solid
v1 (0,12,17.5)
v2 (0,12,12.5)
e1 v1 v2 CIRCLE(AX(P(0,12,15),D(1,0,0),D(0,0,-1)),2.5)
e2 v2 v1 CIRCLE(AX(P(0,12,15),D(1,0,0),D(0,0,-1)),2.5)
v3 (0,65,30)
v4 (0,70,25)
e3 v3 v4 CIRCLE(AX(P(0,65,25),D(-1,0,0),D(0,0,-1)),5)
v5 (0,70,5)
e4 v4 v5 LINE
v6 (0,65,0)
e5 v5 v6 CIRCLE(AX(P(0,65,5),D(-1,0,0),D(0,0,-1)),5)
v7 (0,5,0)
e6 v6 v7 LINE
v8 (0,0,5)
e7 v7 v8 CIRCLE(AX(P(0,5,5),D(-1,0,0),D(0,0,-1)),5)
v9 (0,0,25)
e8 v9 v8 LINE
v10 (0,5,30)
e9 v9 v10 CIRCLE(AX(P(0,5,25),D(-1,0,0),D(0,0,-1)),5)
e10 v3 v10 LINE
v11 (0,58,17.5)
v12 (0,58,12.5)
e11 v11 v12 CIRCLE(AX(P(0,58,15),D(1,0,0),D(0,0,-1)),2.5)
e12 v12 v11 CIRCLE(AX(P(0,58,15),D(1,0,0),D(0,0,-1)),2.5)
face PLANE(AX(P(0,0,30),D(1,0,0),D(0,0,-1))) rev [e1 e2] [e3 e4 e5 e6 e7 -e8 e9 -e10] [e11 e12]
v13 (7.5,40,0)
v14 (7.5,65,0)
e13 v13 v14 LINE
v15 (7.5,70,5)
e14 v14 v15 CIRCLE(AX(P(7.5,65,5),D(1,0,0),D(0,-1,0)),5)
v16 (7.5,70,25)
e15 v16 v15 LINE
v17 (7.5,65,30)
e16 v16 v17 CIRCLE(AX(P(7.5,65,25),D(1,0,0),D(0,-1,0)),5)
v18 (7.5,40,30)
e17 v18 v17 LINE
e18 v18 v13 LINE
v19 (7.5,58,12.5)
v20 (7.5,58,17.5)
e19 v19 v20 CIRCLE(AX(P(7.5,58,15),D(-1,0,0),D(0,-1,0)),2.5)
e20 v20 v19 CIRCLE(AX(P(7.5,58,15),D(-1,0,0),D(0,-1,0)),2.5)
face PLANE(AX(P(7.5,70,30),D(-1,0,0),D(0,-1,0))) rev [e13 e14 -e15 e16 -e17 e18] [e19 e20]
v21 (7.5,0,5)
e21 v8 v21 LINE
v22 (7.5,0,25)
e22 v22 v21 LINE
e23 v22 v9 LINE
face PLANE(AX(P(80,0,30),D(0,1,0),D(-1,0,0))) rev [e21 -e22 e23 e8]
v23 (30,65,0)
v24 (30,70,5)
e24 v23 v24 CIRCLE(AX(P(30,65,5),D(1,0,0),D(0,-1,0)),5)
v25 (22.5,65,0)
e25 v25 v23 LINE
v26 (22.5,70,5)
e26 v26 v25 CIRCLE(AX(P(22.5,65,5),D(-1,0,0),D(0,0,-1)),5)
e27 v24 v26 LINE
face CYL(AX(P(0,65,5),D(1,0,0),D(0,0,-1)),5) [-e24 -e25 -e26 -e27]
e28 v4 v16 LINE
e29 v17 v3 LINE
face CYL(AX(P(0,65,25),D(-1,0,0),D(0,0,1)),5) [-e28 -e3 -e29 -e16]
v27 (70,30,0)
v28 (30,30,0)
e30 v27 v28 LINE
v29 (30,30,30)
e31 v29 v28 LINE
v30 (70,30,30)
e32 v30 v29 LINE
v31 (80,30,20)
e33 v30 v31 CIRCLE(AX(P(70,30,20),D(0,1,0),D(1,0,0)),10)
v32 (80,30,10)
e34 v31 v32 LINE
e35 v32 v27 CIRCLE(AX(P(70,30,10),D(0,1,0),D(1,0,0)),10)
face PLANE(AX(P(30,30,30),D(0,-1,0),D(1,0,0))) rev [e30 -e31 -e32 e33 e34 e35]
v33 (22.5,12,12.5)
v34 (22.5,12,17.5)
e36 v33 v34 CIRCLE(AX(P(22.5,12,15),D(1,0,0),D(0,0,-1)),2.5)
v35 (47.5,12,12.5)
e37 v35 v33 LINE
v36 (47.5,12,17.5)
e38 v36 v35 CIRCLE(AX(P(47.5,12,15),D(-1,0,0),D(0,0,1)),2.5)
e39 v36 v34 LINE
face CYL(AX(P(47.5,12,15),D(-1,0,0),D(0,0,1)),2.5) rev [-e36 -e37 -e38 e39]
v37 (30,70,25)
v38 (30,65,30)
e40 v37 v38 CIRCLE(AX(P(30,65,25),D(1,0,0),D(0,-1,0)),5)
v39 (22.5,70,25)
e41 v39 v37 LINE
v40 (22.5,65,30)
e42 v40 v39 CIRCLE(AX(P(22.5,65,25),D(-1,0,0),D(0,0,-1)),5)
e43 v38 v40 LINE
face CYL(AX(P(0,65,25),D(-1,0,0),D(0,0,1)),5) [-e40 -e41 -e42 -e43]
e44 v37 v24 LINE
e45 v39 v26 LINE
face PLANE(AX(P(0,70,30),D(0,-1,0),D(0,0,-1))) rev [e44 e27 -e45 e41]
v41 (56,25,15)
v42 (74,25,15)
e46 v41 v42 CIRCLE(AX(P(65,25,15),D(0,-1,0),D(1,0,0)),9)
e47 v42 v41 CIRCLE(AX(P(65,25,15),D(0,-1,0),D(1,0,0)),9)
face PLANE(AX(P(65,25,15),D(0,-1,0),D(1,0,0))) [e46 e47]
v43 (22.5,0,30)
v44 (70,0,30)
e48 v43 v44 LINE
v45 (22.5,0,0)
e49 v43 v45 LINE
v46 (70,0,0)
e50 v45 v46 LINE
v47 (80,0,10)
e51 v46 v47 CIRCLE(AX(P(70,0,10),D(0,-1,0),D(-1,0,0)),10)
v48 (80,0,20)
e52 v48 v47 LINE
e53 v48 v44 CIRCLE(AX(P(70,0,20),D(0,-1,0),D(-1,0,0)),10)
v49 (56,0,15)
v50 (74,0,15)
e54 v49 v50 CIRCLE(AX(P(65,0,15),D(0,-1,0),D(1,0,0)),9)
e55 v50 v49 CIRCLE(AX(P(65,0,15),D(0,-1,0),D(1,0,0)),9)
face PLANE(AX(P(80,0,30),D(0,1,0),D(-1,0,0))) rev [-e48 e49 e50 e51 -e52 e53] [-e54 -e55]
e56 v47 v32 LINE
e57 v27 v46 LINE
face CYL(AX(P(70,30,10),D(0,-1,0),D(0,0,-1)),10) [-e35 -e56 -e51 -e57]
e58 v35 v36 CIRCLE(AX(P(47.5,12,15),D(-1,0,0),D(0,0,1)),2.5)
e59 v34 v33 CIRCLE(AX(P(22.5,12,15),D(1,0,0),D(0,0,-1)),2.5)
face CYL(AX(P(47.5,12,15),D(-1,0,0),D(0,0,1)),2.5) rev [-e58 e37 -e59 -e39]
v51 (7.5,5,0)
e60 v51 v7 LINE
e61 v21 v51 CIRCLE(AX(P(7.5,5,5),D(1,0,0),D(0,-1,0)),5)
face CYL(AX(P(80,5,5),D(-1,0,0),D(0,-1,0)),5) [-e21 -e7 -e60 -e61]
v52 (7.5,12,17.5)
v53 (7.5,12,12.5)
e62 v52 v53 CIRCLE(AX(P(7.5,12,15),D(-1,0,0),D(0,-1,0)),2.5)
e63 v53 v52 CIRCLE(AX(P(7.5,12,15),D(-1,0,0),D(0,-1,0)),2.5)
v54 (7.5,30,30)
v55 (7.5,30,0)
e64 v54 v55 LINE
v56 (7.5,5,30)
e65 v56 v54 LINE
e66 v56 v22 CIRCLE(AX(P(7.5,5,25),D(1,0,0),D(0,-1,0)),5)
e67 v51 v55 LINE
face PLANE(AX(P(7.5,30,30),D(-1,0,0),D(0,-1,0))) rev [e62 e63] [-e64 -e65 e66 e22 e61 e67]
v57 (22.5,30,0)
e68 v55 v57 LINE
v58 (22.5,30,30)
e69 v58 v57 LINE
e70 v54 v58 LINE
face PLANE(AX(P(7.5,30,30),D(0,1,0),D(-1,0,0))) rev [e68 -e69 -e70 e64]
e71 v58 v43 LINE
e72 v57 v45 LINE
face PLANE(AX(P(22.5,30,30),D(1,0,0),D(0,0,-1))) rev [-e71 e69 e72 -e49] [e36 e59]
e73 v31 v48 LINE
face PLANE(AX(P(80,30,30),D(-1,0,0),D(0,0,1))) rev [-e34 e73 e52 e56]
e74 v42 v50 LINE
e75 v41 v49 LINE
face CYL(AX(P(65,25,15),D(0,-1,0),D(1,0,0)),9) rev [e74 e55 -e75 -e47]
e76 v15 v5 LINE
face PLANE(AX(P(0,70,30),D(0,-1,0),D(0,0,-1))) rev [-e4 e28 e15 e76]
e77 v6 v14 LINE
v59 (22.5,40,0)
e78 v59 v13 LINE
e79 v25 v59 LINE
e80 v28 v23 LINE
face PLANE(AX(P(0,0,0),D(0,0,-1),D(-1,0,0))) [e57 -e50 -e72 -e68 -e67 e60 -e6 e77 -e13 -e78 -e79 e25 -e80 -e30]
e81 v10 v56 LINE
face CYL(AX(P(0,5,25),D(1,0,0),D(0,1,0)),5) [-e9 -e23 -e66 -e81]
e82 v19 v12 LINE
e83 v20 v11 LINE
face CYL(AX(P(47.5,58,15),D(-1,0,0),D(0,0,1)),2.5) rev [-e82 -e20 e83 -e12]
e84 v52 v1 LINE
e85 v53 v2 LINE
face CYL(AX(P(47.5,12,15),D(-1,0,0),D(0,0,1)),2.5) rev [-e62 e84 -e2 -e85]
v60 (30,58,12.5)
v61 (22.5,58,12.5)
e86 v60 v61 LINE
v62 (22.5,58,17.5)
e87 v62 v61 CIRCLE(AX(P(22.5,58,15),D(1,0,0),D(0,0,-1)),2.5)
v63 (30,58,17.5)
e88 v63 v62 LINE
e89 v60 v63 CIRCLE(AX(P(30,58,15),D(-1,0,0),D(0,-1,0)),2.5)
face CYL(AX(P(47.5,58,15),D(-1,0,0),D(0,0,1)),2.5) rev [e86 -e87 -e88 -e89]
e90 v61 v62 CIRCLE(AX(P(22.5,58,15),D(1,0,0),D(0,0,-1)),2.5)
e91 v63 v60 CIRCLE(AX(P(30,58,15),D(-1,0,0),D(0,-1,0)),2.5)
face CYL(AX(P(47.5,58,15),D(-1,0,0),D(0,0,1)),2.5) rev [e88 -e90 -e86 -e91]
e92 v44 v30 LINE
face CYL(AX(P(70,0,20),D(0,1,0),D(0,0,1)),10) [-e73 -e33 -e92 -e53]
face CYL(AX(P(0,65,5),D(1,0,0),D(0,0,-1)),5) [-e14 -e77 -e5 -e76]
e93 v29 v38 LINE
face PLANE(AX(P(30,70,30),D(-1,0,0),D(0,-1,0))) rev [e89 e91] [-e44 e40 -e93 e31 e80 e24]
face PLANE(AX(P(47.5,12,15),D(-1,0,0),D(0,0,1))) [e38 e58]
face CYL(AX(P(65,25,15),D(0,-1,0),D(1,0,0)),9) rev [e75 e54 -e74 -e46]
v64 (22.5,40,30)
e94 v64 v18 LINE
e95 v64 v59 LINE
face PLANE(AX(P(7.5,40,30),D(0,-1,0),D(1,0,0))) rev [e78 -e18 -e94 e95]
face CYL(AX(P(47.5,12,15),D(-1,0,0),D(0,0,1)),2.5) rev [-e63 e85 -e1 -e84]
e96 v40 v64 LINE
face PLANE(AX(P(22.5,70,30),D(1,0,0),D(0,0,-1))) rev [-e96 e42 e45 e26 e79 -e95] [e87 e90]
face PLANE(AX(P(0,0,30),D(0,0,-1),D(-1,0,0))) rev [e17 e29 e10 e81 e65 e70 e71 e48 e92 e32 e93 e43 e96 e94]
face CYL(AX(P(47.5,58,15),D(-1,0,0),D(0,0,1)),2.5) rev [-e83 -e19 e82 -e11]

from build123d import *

# Parameters (mm, degrees)
BOSS_EXTRUDE1_DEPTH = 30
SKETCH4_R           = 9
CUT_EXTRUDE2_DEPTH  = 25
SKETCH5_W           = 15
SKETCH5_H           = 30
CUT_EXTRUDE3_DEPTH  = 111.453610172
SKETCH6_R           = 2.5
CUT_EXTRUDE4_DEPTH  = 25
FILLET1_R           = 5
FILLET2_R           = 10


with BuildPart() as part:
    # Sketch1 → Boss-Extrude1 (new body)
    with BuildSketch(Plane.XY):
        Polygon((0, 0), (0, 70), (30, 70), (30, 30), (80, 30), (80, 0), align=None)
    extrude(amount=BOSS_EXTRUDE1_DEPTH)

    # Sketch4 → Cut-Extrude2 (cut)
    with BuildSketch(Plane(origin=(0, 0, 0), x_dir=(-1, 0, 0), z_dir=(0, -1, 0))):
        with Locations(Location((-65, -15, 0), (0, 0, 180))):
            Circle(SKETCH4_R)
    extrude(amount=-CUT_EXTRUDE2_DEPTH, mode=Mode.SUBTRACT)

    # Sketch5 → Cut-Extrude3 (cut, through all)
    with BuildSketch(Plane(origin=(0, 0, 0), x_dir=(-1, 0, 0), z_dir=(0, 0, -1))):
        with Locations((-15, 55)):
            Rectangle(SKETCH5_W, SKETCH5_H)
        with Locations((-15, 15)):
            Rectangle(SKETCH5_W, SKETCH5_H)
    extrude(amount=-CUT_EXTRUDE3_DEPTH, mode=Mode.SUBTRACT)

    # Sketch6 → Cut-Extrude4 (cut, symmetric)
    with BuildSketch(Plane.ZY.offset(-22.5)):
        with Locations(Location((15, 58, 0), (0, 0, 270))):
            Circle(SKETCH6_R)
        with Locations((15, 12)):
            Circle(SKETCH6_R)
    extrude(amount=CUT_EXTRUDE4_DEPTH, both=True, mode=Mode.SUBTRACT)

    # Fillet1
    fillet1_edges = [part.edges().sort_by_distance(p)[0] for p in [
        (26.25, 70, 30),
        (3.75, 70, 0),
        (3.75, 70, 30),
        (3.75, 0, 30),
        (26.25, 70, 0),
        (3.75, 0, 0),
    ]]
    fillet(fillet1_edges, radius=FILLET1_R)

    # Fillet2
    fillet2_edges = [part.edges().sort_by_distance(p)[0] for p in [
        (80, 15, 30),
        (80, 15, 0),
    ]]
    fillet(fillet2_edges, radius=FILLET2_R)


solid = part.part
